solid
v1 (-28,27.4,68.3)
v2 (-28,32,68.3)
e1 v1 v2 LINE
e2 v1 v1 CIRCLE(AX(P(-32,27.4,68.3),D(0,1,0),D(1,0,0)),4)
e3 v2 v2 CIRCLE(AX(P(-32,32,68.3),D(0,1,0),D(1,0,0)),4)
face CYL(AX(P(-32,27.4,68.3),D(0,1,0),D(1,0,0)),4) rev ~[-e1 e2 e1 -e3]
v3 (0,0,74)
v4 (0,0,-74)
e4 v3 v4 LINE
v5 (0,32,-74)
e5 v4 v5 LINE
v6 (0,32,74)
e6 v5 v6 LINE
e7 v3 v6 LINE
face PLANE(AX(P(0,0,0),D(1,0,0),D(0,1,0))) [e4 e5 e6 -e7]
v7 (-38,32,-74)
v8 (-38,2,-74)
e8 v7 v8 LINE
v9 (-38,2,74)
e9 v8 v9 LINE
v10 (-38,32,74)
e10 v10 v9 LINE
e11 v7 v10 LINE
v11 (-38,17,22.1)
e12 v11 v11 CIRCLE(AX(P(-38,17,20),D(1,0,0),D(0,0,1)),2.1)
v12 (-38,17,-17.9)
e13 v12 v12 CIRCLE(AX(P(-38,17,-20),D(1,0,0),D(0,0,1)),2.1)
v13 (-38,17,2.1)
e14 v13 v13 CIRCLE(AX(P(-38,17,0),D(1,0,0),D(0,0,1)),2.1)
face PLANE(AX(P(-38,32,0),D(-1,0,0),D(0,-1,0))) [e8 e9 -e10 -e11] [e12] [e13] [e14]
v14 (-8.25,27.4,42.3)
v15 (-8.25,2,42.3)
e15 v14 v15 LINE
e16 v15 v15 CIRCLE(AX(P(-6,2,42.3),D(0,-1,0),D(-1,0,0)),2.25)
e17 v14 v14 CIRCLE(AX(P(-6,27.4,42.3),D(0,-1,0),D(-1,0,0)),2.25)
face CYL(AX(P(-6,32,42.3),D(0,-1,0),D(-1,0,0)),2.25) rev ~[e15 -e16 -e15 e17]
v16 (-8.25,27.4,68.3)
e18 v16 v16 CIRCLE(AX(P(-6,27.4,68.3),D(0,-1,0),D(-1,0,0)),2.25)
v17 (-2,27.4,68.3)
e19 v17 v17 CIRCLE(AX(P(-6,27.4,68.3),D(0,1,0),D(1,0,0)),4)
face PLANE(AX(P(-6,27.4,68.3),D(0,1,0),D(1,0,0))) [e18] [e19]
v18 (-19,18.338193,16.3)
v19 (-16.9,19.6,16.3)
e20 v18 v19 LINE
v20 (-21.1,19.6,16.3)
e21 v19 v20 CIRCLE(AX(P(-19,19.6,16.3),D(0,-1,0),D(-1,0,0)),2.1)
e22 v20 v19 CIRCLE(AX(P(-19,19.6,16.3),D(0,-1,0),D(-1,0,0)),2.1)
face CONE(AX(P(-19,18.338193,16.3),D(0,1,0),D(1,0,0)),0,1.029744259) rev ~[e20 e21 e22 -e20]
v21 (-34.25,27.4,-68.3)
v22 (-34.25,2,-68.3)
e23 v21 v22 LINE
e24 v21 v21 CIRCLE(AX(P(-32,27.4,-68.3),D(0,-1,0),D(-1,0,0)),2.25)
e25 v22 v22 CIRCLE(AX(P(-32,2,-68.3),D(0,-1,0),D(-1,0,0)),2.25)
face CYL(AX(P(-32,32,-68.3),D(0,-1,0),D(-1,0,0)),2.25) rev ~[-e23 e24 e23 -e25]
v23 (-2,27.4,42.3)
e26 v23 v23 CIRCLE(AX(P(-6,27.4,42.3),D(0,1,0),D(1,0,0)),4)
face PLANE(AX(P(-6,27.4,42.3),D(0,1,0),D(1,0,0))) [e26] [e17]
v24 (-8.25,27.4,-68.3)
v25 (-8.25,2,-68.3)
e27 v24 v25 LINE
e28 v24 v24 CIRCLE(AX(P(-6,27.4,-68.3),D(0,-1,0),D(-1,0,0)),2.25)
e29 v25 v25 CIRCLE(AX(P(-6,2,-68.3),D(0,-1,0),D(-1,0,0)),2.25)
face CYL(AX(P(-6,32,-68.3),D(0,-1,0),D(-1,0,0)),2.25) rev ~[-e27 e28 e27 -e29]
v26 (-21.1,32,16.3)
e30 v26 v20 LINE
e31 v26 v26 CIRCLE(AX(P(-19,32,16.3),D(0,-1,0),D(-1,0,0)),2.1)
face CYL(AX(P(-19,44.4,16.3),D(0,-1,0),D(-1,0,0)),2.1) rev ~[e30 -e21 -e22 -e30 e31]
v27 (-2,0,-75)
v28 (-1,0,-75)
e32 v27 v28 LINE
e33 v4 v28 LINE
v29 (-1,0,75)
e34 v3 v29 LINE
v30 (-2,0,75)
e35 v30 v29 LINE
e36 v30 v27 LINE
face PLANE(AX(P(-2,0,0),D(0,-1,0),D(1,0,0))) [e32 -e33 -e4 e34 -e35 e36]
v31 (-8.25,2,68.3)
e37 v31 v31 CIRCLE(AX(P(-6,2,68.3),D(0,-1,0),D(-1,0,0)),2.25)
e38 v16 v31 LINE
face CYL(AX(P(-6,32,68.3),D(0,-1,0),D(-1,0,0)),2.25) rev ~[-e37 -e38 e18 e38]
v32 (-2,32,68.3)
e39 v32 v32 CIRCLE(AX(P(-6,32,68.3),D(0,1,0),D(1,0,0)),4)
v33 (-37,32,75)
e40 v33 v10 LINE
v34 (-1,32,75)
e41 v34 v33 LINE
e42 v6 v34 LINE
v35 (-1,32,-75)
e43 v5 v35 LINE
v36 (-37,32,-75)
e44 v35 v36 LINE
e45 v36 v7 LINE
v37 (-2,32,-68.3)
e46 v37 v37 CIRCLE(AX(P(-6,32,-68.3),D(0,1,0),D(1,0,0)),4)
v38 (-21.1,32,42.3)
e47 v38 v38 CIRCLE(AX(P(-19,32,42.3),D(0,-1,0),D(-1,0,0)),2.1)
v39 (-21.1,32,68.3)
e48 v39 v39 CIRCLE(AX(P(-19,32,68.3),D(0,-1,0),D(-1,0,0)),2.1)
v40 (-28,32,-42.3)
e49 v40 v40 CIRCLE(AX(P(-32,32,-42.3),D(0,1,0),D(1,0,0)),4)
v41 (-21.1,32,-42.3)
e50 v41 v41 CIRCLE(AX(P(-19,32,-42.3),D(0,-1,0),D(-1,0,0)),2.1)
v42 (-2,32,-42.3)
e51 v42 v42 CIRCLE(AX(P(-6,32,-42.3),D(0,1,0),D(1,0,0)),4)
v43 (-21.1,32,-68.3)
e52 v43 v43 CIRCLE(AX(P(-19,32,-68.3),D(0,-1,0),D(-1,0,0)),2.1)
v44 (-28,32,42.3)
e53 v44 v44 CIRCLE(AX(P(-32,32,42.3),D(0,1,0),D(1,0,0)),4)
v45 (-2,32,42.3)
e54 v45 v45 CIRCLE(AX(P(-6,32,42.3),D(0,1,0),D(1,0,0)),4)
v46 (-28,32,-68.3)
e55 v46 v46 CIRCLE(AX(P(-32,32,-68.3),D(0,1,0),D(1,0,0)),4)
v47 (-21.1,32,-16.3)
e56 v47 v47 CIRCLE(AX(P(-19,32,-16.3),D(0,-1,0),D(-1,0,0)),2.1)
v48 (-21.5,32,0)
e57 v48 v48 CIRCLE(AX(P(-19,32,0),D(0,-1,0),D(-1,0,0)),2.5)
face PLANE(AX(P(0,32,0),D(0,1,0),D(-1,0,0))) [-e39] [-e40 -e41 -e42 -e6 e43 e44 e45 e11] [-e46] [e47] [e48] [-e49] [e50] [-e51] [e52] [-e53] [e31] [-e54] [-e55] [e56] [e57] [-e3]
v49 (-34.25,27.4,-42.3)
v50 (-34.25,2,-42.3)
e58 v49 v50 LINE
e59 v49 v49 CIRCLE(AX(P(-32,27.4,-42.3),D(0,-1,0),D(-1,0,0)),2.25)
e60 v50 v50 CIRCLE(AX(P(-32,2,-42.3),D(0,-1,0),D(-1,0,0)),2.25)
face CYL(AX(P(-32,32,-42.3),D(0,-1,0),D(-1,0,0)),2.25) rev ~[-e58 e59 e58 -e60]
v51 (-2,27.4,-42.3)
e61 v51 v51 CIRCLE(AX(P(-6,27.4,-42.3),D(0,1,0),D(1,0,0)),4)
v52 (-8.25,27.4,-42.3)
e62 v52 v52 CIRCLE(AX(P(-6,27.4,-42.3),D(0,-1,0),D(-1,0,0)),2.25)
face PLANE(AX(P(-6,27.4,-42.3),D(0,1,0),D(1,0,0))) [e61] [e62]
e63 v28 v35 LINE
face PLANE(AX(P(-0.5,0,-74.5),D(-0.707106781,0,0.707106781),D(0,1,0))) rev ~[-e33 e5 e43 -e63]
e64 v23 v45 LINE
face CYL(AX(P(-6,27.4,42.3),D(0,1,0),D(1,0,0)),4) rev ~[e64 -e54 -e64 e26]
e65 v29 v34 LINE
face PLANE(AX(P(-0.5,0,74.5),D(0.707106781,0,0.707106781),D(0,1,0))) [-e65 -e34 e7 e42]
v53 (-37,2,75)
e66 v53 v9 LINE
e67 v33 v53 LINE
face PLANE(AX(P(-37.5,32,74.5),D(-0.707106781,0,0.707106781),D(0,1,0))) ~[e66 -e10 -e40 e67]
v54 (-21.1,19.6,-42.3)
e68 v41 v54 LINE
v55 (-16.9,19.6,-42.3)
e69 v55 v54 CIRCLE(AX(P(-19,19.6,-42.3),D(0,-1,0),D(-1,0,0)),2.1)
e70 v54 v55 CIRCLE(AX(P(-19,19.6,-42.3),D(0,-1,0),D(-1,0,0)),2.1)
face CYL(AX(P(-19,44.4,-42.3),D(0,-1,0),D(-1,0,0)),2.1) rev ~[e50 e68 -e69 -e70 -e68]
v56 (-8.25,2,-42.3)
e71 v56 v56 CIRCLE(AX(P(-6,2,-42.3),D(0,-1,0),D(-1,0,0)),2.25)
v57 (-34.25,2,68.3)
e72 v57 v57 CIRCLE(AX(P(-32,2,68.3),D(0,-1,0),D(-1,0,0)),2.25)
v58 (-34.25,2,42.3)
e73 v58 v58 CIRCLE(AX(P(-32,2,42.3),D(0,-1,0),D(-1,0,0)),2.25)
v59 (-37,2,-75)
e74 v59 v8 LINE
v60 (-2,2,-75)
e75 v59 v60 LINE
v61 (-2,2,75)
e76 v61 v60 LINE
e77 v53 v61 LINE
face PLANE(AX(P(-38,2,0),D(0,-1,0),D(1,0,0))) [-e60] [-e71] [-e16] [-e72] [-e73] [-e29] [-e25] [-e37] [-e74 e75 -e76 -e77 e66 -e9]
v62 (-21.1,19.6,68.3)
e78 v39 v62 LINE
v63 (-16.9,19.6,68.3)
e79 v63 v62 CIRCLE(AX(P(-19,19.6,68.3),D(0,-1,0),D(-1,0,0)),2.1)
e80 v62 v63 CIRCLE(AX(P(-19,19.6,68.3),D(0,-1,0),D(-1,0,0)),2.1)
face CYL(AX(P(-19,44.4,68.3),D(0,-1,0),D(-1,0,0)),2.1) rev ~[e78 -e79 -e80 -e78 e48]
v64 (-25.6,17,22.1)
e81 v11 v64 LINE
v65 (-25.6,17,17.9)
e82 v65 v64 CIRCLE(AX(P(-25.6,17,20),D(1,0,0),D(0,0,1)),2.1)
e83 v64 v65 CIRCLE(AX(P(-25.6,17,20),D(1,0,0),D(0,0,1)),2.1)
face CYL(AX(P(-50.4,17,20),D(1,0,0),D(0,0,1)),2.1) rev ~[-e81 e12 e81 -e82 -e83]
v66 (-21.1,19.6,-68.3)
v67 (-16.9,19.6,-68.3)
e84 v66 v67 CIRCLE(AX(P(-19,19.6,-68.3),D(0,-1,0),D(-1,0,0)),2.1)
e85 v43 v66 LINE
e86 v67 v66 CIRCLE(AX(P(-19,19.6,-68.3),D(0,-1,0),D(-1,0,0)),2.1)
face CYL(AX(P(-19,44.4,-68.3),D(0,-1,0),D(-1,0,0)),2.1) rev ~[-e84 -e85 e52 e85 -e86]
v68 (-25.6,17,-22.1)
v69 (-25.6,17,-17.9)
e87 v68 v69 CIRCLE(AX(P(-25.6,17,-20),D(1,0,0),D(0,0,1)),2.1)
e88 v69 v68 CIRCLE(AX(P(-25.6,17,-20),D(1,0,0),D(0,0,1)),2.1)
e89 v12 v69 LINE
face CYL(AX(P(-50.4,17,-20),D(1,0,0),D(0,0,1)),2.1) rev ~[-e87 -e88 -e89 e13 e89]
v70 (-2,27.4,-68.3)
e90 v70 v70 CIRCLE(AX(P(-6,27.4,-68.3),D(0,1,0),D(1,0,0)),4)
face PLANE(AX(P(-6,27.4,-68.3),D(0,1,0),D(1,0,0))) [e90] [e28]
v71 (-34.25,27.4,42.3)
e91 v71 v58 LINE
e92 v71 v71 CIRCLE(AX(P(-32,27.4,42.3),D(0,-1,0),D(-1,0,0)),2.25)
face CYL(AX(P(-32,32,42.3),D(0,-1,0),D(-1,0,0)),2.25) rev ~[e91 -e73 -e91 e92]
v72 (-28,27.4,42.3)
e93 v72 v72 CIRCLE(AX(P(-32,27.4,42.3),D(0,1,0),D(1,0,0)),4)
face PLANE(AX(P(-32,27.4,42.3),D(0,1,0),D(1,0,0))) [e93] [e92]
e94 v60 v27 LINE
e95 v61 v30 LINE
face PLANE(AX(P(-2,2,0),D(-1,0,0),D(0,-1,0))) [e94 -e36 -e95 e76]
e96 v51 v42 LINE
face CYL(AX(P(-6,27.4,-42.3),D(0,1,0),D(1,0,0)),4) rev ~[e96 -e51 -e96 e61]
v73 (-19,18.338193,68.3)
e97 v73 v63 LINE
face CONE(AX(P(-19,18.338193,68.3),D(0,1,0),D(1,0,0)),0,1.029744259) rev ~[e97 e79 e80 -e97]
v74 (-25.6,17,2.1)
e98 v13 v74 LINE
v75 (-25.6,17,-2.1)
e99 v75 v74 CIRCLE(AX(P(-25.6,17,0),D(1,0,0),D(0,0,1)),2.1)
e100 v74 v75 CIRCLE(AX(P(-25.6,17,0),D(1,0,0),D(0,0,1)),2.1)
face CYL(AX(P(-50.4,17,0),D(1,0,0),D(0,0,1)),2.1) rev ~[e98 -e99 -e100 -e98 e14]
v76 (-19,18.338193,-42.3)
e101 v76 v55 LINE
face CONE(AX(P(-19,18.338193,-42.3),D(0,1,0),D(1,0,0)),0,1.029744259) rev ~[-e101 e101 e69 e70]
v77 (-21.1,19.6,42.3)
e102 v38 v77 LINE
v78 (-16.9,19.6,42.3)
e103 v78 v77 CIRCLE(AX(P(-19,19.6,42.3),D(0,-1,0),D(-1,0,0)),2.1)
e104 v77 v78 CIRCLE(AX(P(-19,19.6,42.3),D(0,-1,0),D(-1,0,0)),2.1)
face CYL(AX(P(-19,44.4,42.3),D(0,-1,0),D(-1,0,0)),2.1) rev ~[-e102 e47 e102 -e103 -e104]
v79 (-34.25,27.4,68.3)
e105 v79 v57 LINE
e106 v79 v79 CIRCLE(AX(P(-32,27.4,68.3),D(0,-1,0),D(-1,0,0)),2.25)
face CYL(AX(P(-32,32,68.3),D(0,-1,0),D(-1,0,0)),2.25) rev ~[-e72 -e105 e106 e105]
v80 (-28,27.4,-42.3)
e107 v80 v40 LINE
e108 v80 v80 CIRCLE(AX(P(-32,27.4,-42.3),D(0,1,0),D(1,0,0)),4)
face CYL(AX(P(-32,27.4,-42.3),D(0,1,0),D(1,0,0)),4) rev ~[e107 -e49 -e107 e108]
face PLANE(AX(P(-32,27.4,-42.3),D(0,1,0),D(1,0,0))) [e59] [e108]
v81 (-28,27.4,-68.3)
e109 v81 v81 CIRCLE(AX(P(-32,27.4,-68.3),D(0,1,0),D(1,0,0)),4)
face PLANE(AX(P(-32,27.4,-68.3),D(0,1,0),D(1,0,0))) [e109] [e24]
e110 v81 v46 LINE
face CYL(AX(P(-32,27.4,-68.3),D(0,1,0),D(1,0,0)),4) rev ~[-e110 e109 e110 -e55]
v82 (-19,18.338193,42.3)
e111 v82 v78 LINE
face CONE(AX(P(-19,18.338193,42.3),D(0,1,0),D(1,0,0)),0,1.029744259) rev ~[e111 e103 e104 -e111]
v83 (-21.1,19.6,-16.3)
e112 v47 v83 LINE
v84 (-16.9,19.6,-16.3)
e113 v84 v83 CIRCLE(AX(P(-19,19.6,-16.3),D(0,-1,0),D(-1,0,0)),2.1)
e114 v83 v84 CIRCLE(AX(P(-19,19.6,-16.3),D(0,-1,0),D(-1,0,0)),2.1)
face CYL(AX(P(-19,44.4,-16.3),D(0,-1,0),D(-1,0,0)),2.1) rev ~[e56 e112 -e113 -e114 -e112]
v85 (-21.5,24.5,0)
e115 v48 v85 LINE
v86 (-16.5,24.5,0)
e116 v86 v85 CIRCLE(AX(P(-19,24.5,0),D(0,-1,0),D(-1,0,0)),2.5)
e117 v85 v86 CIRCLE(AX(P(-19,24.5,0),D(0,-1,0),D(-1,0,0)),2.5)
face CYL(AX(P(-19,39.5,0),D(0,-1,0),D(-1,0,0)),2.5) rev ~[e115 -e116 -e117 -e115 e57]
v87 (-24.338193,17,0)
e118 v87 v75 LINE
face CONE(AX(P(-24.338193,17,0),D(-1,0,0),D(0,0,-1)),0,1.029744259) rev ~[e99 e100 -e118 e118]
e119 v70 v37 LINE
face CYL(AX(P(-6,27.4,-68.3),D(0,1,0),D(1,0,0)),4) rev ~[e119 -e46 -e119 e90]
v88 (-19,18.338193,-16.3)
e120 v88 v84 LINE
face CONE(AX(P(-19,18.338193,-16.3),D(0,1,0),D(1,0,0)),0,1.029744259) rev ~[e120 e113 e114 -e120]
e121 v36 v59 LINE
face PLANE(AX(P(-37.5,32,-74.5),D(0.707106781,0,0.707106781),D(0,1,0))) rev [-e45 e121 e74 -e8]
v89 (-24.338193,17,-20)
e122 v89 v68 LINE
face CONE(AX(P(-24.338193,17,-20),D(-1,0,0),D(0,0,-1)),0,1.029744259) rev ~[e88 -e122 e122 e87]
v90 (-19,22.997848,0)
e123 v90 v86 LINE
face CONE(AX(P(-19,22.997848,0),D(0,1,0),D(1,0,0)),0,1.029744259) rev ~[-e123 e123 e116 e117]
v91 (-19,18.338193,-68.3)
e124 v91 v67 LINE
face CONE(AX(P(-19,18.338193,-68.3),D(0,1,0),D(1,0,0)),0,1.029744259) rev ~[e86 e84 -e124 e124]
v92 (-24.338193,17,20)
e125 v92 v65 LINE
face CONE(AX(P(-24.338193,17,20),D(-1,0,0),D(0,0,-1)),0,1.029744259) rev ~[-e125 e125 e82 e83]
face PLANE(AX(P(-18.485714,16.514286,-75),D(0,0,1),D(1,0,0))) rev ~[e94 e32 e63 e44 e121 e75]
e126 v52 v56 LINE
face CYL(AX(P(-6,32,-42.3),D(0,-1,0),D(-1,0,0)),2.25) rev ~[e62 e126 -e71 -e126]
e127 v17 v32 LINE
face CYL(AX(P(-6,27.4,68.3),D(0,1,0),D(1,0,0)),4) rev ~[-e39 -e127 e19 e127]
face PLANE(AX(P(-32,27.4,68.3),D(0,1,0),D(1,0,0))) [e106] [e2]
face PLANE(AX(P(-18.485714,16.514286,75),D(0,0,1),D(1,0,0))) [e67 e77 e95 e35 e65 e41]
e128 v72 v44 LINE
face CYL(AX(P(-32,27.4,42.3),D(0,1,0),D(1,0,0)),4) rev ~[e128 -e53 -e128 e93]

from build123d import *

# Parameters (mm, degrees)
BOSS_EXTRUDE1_DEPTH                                 = 75
HOLE_SIZE_BY_SOCKET_HEAD_CAP_SCREW_TYPE_D           = 4.5
HOLE_SIZE_BY_SOCKET_HEAD_CAP_SCREW_TYPE_CBORE_D     = 8
HOLE_SIZE_BY_SOCKET_HEAD_CAP_SCREW_TYPE_CBORE_DEPTH = 4.6
M5_TAPPED_HOLE1_D                                   = 4.2
M5_TAPPED_HOLE1_DEPTH                               = 12.4
M5_TAPPED_HOLE1_TIP                                 = 1.2618073
M5_TAPPED_HOLE2_D                                   = 4.2
M5_TAPPED_HOLE2_DEPTH                               = 12.4
M5_TAPPED_HOLE2_TIP                                 = 1.2618073
CHAMFER1_SIZE                                       = 1
SIZE_MM_BLIND_PIN_HOLE1_D                           = 5
SIZE_MM_BLIND_PIN_HOLE1_DEPTH                       = 7.5
SIZE_MM_BLIND_PIN_HOLE1_TIP                         = 1.502151548


with BuildPart() as part:
    # Sketch1 → Boss-Extrude1 (new, symmetric)
    with BuildSketch(Plane.XY):
        Polygon((0, 0), (0, 32), (-38, 32), (-38, 2), (-2, 2), (-2, 0), align=None)
    extrude(amount=BOSS_EXTRUDE1_DEPTH, both=True)

    # Hole Size (by socket head cap screw type)1 (through all)
    with Locations(Plane(origin=(0, 32, 0), x_dir=(1, 0, 0), z_dir=(0, 1, 0))):
        with Locations((-32, -68.3), (-32, 68.3), (-6, 42.3), (-32, 42.3), (-6, 68.3), (-6, -68.3), (-6, -42.3), (-32, -42.3)):
            CounterBoreHole(HOLE_SIZE_BY_SOCKET_HEAD_CAP_SCREW_TYPE_D / 2, HOLE_SIZE_BY_SOCKET_HEAD_CAP_SCREW_TYPE_CBORE_D / 2, HOLE_SIZE_BY_SOCKET_HEAD_CAP_SCREW_TYPE_CBORE_DEPTH)

    # M5 Tapped Hole1
    with Locations(Plane(origin=(-38, 0, 0), x_dir=(0, 0, -1), z_dir=(-1, 0, 0))):
        with Locations((0, -17), (-20, -17), (20, -17)):
            Hole(M5_TAPPED_HOLE1_D / 2, depth=M5_TAPPED_HOLE1_DEPTH)
            with Locations((0, 0, -(M5_TAPPED_HOLE1_DEPTH + M5_TAPPED_HOLE1_TIP / 2))):  # 118° drill point
                Cone(0, M5_TAPPED_HOLE1_D / 2, M5_TAPPED_HOLE1_TIP, mode=Mode.SUBTRACT)

    # M5 Tapped Hole2
    with Locations(Plane(origin=(0, 32, 0), x_dir=(1, 0, 0), z_dir=(0, 1, 0))):
        with Locations((-19, -16.3), (-19, 68.3), (-19, 42.3), (-19, -42.3), (-19, -68.3), (-19, 16.3)):
            Hole(M5_TAPPED_HOLE2_D / 2, depth=M5_TAPPED_HOLE2_DEPTH)
            with Locations((0, 0, -(M5_TAPPED_HOLE2_DEPTH + M5_TAPPED_HOLE2_TIP / 2))):  # 118° drill point
                Cone(0, M5_TAPPED_HOLE2_D / 2, M5_TAPPED_HOLE2_TIP, mode=Mode.SUBTRACT)

    # Chamfer1
    chamfer1_edges = [part.edges().sort_by_distance(p)[0] for p in [
        (-38, 17, 75),
        (-38, 17, -75),
        (0, 16, -75),
        (0, 16, 75),
    ]]
    chamfer(chamfer1_edges, length=CHAMFER1_SIZE)

    # Size mm Blind Pin Hole1
    with Locations(Plane(origin=(0, 32, 0), x_dir=(1, 0, 0), z_dir=(0, 1, 0))):
        with Locations((-19, 0)):
            Hole(SIZE_MM_BLIND_PIN_HOLE1_D / 2, depth=SIZE_MM_BLIND_PIN_HOLE1_DEPTH)
            with Locations((0, 0, -(SIZE_MM_BLIND_PIN_HOLE1_DEPTH + SIZE_MM_BLIND_PIN_HOLE1_TIP / 2))):  # 118° drill point
                Cone(0, SIZE_MM_BLIND_PIN_HOLE1_D / 2, SIZE_MM_BLIND_PIN_HOLE1_TIP, mode=Mode.SUBTRACT)


solid = part.part
